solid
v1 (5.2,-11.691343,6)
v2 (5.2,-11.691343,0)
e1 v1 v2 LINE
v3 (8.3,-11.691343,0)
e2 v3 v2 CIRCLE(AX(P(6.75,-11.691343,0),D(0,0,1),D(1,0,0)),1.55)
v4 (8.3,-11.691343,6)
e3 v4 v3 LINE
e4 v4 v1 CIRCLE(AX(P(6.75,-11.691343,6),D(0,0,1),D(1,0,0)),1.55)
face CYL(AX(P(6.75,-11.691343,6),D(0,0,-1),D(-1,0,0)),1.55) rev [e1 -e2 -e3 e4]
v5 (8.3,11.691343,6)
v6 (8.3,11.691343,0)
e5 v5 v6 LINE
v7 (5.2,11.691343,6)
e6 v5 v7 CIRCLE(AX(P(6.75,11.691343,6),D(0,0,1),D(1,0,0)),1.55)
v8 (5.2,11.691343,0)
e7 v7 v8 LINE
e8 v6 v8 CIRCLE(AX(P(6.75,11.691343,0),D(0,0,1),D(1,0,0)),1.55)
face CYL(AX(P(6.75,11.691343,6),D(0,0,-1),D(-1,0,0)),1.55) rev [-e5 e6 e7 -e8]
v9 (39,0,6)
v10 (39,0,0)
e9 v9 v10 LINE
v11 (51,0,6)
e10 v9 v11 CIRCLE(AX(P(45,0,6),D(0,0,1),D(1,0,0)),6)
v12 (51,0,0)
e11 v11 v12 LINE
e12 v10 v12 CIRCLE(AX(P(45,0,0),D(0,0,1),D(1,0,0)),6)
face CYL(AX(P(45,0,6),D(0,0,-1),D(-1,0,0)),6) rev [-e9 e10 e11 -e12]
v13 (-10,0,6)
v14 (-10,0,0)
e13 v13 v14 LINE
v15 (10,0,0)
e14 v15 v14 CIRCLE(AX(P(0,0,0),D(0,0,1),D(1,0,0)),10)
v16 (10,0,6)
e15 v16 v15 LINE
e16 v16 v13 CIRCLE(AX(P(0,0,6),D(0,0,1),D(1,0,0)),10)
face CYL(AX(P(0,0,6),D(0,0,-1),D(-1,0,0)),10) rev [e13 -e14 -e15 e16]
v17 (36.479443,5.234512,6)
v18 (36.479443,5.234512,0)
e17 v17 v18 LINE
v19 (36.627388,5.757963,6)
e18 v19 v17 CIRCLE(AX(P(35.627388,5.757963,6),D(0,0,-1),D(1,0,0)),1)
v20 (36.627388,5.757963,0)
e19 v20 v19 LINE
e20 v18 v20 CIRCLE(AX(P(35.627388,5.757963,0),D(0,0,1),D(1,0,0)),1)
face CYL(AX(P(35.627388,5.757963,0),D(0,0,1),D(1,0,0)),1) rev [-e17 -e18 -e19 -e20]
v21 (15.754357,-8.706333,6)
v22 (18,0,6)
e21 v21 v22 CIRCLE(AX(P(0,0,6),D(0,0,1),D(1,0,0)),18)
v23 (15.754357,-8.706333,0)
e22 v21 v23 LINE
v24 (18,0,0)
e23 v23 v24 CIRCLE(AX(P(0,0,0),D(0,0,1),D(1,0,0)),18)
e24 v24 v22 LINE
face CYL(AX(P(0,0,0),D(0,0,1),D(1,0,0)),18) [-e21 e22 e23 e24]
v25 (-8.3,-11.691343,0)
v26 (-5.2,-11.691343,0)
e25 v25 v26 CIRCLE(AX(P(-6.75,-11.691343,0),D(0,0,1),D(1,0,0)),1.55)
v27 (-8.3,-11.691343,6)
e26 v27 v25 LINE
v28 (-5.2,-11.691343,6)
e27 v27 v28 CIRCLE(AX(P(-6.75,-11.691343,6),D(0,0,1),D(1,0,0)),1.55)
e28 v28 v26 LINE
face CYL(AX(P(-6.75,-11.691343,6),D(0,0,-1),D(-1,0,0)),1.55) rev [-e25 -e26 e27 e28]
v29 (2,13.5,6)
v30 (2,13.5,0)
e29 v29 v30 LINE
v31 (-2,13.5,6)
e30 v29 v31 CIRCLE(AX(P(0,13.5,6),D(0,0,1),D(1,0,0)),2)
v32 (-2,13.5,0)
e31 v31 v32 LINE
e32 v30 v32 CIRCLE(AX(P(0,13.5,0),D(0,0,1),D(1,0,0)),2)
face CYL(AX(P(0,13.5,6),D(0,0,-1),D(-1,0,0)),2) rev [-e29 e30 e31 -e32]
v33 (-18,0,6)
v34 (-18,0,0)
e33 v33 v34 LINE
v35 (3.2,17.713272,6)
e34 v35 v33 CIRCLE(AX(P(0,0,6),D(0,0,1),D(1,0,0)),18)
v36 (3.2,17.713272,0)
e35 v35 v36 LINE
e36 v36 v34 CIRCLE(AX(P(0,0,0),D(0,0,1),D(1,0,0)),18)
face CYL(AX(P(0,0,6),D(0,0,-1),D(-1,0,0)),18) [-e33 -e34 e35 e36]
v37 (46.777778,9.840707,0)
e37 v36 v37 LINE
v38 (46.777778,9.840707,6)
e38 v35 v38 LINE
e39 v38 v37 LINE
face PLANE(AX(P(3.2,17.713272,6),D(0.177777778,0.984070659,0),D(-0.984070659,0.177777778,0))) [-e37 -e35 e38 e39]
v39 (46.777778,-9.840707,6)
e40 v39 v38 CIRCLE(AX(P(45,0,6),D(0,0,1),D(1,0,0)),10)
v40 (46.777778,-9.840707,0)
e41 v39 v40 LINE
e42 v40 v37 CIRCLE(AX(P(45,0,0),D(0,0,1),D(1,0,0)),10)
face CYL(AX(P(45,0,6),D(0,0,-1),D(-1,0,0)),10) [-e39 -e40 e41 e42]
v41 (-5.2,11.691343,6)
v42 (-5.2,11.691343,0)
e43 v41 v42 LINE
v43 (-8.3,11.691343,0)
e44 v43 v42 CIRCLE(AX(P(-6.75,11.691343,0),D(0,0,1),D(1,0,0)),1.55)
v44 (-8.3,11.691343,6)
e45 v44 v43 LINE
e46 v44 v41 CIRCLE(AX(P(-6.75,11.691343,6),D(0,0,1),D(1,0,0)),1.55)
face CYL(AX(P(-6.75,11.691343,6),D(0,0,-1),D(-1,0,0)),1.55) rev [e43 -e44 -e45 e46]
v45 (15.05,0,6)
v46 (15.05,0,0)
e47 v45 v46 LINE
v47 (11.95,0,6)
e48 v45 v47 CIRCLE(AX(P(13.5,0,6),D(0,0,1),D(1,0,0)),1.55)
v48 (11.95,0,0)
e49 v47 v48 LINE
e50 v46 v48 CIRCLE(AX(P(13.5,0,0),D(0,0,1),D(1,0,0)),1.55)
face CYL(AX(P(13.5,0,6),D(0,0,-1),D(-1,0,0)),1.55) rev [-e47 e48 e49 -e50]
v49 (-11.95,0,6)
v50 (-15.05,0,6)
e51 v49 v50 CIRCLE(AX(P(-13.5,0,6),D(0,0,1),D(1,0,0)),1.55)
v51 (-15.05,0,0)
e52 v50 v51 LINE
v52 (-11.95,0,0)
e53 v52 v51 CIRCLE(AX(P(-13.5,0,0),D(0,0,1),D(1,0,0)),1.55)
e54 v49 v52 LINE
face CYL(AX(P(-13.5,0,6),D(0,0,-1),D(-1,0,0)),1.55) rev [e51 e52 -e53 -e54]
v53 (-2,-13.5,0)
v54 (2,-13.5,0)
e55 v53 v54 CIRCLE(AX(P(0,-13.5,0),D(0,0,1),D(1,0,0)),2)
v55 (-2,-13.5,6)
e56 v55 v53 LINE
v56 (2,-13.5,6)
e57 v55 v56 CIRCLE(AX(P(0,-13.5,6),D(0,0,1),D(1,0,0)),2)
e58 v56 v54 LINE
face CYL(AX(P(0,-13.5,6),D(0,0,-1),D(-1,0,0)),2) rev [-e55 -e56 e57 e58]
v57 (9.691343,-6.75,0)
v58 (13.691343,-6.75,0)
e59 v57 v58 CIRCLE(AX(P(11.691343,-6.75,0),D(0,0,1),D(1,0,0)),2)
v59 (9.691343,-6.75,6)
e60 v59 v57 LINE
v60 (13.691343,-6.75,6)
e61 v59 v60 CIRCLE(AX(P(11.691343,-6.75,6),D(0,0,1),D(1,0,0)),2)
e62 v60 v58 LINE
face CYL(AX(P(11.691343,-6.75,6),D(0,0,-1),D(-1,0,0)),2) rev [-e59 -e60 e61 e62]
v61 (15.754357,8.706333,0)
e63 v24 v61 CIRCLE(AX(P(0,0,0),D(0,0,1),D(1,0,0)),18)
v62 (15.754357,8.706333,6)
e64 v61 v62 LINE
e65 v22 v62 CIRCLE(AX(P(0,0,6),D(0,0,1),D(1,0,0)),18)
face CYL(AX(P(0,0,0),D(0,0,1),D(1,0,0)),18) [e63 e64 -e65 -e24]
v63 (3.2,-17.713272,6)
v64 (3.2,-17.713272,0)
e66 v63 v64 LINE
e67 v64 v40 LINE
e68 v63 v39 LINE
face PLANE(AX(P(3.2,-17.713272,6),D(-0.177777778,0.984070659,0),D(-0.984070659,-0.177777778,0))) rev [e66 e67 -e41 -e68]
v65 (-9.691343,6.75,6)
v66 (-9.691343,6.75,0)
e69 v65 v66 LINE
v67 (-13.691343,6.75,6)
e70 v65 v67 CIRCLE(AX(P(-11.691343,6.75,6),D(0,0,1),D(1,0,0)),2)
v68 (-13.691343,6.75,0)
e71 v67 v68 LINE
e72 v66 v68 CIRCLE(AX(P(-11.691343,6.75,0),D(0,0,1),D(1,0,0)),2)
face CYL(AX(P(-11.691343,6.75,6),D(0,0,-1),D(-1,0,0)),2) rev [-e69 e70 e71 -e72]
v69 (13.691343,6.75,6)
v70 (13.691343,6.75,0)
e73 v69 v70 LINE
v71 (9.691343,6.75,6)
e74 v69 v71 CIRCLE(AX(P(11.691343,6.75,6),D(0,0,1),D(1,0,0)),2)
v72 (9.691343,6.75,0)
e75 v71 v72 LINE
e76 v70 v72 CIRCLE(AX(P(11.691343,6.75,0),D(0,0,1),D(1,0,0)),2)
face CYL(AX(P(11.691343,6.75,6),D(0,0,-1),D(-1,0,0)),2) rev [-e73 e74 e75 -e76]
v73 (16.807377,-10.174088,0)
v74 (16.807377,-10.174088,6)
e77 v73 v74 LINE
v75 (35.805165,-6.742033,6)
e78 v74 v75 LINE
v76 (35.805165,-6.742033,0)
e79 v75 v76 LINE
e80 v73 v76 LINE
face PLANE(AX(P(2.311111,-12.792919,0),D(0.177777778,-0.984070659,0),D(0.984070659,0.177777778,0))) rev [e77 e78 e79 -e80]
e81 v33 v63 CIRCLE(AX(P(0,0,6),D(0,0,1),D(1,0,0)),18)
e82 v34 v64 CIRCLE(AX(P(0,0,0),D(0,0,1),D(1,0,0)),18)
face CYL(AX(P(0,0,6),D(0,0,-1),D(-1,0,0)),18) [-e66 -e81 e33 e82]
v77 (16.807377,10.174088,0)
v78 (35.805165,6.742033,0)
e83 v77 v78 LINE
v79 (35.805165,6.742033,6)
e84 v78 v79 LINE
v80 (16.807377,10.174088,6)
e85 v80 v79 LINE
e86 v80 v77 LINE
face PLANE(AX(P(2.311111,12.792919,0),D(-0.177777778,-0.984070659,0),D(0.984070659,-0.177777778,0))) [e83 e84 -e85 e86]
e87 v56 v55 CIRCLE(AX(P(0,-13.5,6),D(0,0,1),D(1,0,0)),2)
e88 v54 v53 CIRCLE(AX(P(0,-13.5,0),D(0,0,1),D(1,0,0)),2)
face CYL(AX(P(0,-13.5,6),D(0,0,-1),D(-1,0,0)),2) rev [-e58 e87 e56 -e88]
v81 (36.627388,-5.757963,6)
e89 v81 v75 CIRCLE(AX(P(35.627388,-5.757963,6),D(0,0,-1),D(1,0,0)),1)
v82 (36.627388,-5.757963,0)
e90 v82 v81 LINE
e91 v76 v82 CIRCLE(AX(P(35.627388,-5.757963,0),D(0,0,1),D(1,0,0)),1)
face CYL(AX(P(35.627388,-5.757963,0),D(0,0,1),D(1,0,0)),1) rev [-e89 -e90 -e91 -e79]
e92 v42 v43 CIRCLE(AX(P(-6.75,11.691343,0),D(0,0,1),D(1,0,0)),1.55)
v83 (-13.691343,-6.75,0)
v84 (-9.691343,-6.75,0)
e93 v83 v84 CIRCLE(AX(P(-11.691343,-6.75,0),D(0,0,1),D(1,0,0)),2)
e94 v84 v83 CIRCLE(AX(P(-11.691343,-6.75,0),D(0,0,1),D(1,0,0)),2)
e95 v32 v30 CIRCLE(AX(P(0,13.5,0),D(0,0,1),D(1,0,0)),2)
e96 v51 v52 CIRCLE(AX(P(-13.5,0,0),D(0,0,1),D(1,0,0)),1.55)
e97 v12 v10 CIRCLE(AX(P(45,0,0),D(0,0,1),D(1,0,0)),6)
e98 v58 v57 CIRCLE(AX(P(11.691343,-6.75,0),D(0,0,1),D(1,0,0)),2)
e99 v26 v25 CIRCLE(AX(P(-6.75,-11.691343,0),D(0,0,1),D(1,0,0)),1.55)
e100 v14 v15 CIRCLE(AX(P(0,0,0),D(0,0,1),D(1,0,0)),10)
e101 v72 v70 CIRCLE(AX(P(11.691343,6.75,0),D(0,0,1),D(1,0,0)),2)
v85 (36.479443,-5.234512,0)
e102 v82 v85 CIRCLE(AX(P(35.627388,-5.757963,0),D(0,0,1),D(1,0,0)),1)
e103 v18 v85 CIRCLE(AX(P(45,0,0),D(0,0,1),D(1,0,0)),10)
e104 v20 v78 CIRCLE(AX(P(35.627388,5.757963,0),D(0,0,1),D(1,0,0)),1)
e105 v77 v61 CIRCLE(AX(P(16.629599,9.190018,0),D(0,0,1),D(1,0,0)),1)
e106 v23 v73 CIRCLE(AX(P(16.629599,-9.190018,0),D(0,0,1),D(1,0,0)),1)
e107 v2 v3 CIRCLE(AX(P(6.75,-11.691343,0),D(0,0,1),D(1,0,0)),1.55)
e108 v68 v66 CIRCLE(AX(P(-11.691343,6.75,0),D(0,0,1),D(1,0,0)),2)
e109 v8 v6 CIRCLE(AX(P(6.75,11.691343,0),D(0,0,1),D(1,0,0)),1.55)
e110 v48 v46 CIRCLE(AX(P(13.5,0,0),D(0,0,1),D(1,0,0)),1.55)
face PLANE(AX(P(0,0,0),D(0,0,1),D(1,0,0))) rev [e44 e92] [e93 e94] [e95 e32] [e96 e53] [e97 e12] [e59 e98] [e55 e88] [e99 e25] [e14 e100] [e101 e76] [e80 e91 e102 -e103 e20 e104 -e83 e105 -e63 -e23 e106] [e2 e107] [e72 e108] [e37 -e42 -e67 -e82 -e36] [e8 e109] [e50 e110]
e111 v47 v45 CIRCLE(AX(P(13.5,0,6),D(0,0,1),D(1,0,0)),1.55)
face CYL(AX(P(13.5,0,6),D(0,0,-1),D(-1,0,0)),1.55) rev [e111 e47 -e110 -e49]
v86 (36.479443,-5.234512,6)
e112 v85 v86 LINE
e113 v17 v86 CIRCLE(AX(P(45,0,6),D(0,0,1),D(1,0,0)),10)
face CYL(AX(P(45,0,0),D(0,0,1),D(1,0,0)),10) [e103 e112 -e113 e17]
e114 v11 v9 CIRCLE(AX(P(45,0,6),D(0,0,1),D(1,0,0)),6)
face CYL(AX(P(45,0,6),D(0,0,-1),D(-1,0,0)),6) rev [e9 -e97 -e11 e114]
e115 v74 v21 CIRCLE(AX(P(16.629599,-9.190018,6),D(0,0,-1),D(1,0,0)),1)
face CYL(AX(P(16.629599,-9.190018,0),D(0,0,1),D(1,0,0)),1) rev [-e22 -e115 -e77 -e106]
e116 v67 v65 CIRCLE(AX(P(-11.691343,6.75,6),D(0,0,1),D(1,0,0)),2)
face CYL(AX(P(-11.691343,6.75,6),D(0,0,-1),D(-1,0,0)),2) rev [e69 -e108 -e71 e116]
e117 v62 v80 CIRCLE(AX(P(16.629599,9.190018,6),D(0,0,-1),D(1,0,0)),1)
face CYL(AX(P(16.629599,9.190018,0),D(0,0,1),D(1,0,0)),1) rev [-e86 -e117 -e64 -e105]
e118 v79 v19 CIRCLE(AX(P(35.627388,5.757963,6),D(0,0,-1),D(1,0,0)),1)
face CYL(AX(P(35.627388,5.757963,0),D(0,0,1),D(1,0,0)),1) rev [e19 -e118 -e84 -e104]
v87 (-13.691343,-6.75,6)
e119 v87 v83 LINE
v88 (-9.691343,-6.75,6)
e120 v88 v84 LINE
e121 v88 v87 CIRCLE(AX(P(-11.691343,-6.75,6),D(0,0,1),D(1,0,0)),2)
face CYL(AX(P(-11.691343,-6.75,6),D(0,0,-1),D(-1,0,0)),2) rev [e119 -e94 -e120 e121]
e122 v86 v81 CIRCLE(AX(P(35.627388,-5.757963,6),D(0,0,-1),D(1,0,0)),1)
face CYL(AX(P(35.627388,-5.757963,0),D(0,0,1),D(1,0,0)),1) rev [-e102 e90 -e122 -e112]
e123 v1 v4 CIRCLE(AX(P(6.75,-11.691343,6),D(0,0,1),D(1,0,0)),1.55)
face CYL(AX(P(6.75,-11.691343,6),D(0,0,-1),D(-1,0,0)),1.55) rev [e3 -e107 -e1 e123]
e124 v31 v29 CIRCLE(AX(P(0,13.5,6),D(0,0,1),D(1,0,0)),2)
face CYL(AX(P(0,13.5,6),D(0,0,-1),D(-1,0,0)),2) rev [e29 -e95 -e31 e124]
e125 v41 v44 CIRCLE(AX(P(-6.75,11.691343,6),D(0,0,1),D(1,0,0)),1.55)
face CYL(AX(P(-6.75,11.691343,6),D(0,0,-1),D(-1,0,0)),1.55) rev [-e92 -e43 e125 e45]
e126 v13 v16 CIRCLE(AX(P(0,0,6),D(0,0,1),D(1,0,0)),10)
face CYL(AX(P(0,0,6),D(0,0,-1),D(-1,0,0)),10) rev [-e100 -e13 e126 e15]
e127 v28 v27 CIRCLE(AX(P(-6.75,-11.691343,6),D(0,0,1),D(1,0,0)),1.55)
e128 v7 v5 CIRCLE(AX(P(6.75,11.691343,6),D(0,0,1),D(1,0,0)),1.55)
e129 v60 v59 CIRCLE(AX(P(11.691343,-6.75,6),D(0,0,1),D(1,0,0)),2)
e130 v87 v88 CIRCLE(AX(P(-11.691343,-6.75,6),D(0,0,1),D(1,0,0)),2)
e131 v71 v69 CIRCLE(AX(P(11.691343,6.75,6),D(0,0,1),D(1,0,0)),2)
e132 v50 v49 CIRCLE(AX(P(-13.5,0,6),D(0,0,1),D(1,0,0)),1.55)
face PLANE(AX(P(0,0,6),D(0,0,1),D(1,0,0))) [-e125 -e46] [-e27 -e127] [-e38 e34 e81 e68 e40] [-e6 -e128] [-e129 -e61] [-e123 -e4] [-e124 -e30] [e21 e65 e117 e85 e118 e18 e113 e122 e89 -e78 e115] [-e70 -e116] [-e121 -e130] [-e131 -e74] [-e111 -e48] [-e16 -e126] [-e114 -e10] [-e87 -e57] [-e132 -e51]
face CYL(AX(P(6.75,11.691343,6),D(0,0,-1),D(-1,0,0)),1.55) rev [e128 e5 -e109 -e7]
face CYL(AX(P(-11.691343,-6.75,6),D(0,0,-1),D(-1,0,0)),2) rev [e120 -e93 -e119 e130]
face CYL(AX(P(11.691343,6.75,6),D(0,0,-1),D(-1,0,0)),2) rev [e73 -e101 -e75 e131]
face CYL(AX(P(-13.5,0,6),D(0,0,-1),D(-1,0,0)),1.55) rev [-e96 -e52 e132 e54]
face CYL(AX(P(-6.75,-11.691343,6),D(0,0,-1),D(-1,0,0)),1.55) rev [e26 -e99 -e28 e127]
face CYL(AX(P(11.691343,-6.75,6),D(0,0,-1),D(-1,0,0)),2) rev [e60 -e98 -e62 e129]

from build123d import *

# Parameters (mm, degrees)
SKETCH_1_R          = 2
SKETCH_1_R_2        = 1.55
SKETCH_1_R_3        = 10
SKETCH_1_R_4        = 6
EXTRUDE_1_DEPTH     = 6
CUT_EXTRUDE_1_DEPTH = 59.180752831
FILLET_1_R          = 1


with BuildPart() as part:
    # 草图1 → 凸台-拉伸1 (new body)
    with BuildSketch(Plane.XY):
        with BuildLine():
            Line((46.777777778, 9.840706589), (3.2, 17.71327186))
            ThreePointArc((3.2, 17.71327186), (-18, 0), (3.2, -17.71327186))
            Line((3.2, -17.71327186), (46.777777778, -9.840706589))
            ThreePointArc((46.777777778, -9.840706589), (55, 0), (46.777777778, 9.840706589))
        make_face()
        with Locations((0, 13.5)):
            Circle(SKETCH_1_R, mode=Mode.SUBTRACT)
        with Locations((6.75, 11.691342951)):
            Circle(SKETCH_1_R_2, mode=Mode.SUBTRACT)
        with Locations((0, -13.5)):
            Circle(SKETCH_1_R, mode=Mode.SUBTRACT)
        with Locations((-6.75, -11.691342951)):
            Circle(SKETCH_1_R_2, mode=Mode.SUBTRACT)
        with Locations((6.75, -11.691342951)):
            Circle(SKETCH_1_R_2, mode=Mode.SUBTRACT)
        with Locations((-11.691342951, -6.75)):
            Circle(SKETCH_1_R, mode=Mode.SUBTRACT)
        with Locations((11.691342951, -6.75)):
            Circle(SKETCH_1_R, mode=Mode.SUBTRACT)
        with Locations((-13.5, 0)):
            Circle(SKETCH_1_R_2, mode=Mode.SUBTRACT)
        Circle(SKETCH_1_R_3, mode=Mode.SUBTRACT)
        with Locations((-11.691342951, 6.75)):
            Circle(SKETCH_1_R, mode=Mode.SUBTRACT)
        with Locations((13.5, 0)):
            Circle(SKETCH_1_R_2, mode=Mode.SUBTRACT)
        with Locations((11.691342951, 6.75)):
            Circle(SKETCH_1_R, mode=Mode.SUBTRACT)
        with Locations((-6.75, 11.691342951)):
            Circle(SKETCH_1_R_2, mode=Mode.SUBTRACT)
        with Locations((45, 0)):
            Circle(SKETCH_1_R_4, mode=Mode.SUBTRACT)
    extrude(amount=EXTRUDE_1_DEPTH)

    # 草图3 → 切除-拉伸1 (cut, through all)
    with BuildSketch(Plane.XY.offset(6)):
        with BuildLine():
            Line((37.366586992, 6.459954012), (14.562692012, 10.579603082))
            ThreePointArc((14.562692012, 10.579603082), (17.119118789, 5.561993518), (18, 0))
            Line((18, 0), (35, 0))
            ThreePointArc((35, 0), (35.610268106, 3.439903336), (37.366586992, 6.459954012))
        make_face()
        with BuildLine():
            Line((35, 0), (18, 0))
            ThreePointArc((18, 0), (17.119118789, -5.561993518), (14.562692012, -10.579603082))
            Line((14.562692012, -10.579603082), (37.366586992, -6.459954012))
            ThreePointArc((37.366586992, -6.459954012), (35.610268106, -3.439903336), (35, 0))
        make_face()
    extrude(amount=-CUT_EXTRUDE_1_DEPTH, mode=Mode.SUBTRACT)

    # 圆角1
    fillet_1_edges = [part.edges().sort_by_distance(p)[0] for p in [
        (14.562692012, -10.579603082, 3),
        (14.562692012, 10.579603082, 3),
        (37.366586992, 6.459954012, 3),
        (37.366586992, -6.459954012, 3),
    ]]
    fillet(fillet_1_edges, radius=FILLET_1_R)


solid = part.part
